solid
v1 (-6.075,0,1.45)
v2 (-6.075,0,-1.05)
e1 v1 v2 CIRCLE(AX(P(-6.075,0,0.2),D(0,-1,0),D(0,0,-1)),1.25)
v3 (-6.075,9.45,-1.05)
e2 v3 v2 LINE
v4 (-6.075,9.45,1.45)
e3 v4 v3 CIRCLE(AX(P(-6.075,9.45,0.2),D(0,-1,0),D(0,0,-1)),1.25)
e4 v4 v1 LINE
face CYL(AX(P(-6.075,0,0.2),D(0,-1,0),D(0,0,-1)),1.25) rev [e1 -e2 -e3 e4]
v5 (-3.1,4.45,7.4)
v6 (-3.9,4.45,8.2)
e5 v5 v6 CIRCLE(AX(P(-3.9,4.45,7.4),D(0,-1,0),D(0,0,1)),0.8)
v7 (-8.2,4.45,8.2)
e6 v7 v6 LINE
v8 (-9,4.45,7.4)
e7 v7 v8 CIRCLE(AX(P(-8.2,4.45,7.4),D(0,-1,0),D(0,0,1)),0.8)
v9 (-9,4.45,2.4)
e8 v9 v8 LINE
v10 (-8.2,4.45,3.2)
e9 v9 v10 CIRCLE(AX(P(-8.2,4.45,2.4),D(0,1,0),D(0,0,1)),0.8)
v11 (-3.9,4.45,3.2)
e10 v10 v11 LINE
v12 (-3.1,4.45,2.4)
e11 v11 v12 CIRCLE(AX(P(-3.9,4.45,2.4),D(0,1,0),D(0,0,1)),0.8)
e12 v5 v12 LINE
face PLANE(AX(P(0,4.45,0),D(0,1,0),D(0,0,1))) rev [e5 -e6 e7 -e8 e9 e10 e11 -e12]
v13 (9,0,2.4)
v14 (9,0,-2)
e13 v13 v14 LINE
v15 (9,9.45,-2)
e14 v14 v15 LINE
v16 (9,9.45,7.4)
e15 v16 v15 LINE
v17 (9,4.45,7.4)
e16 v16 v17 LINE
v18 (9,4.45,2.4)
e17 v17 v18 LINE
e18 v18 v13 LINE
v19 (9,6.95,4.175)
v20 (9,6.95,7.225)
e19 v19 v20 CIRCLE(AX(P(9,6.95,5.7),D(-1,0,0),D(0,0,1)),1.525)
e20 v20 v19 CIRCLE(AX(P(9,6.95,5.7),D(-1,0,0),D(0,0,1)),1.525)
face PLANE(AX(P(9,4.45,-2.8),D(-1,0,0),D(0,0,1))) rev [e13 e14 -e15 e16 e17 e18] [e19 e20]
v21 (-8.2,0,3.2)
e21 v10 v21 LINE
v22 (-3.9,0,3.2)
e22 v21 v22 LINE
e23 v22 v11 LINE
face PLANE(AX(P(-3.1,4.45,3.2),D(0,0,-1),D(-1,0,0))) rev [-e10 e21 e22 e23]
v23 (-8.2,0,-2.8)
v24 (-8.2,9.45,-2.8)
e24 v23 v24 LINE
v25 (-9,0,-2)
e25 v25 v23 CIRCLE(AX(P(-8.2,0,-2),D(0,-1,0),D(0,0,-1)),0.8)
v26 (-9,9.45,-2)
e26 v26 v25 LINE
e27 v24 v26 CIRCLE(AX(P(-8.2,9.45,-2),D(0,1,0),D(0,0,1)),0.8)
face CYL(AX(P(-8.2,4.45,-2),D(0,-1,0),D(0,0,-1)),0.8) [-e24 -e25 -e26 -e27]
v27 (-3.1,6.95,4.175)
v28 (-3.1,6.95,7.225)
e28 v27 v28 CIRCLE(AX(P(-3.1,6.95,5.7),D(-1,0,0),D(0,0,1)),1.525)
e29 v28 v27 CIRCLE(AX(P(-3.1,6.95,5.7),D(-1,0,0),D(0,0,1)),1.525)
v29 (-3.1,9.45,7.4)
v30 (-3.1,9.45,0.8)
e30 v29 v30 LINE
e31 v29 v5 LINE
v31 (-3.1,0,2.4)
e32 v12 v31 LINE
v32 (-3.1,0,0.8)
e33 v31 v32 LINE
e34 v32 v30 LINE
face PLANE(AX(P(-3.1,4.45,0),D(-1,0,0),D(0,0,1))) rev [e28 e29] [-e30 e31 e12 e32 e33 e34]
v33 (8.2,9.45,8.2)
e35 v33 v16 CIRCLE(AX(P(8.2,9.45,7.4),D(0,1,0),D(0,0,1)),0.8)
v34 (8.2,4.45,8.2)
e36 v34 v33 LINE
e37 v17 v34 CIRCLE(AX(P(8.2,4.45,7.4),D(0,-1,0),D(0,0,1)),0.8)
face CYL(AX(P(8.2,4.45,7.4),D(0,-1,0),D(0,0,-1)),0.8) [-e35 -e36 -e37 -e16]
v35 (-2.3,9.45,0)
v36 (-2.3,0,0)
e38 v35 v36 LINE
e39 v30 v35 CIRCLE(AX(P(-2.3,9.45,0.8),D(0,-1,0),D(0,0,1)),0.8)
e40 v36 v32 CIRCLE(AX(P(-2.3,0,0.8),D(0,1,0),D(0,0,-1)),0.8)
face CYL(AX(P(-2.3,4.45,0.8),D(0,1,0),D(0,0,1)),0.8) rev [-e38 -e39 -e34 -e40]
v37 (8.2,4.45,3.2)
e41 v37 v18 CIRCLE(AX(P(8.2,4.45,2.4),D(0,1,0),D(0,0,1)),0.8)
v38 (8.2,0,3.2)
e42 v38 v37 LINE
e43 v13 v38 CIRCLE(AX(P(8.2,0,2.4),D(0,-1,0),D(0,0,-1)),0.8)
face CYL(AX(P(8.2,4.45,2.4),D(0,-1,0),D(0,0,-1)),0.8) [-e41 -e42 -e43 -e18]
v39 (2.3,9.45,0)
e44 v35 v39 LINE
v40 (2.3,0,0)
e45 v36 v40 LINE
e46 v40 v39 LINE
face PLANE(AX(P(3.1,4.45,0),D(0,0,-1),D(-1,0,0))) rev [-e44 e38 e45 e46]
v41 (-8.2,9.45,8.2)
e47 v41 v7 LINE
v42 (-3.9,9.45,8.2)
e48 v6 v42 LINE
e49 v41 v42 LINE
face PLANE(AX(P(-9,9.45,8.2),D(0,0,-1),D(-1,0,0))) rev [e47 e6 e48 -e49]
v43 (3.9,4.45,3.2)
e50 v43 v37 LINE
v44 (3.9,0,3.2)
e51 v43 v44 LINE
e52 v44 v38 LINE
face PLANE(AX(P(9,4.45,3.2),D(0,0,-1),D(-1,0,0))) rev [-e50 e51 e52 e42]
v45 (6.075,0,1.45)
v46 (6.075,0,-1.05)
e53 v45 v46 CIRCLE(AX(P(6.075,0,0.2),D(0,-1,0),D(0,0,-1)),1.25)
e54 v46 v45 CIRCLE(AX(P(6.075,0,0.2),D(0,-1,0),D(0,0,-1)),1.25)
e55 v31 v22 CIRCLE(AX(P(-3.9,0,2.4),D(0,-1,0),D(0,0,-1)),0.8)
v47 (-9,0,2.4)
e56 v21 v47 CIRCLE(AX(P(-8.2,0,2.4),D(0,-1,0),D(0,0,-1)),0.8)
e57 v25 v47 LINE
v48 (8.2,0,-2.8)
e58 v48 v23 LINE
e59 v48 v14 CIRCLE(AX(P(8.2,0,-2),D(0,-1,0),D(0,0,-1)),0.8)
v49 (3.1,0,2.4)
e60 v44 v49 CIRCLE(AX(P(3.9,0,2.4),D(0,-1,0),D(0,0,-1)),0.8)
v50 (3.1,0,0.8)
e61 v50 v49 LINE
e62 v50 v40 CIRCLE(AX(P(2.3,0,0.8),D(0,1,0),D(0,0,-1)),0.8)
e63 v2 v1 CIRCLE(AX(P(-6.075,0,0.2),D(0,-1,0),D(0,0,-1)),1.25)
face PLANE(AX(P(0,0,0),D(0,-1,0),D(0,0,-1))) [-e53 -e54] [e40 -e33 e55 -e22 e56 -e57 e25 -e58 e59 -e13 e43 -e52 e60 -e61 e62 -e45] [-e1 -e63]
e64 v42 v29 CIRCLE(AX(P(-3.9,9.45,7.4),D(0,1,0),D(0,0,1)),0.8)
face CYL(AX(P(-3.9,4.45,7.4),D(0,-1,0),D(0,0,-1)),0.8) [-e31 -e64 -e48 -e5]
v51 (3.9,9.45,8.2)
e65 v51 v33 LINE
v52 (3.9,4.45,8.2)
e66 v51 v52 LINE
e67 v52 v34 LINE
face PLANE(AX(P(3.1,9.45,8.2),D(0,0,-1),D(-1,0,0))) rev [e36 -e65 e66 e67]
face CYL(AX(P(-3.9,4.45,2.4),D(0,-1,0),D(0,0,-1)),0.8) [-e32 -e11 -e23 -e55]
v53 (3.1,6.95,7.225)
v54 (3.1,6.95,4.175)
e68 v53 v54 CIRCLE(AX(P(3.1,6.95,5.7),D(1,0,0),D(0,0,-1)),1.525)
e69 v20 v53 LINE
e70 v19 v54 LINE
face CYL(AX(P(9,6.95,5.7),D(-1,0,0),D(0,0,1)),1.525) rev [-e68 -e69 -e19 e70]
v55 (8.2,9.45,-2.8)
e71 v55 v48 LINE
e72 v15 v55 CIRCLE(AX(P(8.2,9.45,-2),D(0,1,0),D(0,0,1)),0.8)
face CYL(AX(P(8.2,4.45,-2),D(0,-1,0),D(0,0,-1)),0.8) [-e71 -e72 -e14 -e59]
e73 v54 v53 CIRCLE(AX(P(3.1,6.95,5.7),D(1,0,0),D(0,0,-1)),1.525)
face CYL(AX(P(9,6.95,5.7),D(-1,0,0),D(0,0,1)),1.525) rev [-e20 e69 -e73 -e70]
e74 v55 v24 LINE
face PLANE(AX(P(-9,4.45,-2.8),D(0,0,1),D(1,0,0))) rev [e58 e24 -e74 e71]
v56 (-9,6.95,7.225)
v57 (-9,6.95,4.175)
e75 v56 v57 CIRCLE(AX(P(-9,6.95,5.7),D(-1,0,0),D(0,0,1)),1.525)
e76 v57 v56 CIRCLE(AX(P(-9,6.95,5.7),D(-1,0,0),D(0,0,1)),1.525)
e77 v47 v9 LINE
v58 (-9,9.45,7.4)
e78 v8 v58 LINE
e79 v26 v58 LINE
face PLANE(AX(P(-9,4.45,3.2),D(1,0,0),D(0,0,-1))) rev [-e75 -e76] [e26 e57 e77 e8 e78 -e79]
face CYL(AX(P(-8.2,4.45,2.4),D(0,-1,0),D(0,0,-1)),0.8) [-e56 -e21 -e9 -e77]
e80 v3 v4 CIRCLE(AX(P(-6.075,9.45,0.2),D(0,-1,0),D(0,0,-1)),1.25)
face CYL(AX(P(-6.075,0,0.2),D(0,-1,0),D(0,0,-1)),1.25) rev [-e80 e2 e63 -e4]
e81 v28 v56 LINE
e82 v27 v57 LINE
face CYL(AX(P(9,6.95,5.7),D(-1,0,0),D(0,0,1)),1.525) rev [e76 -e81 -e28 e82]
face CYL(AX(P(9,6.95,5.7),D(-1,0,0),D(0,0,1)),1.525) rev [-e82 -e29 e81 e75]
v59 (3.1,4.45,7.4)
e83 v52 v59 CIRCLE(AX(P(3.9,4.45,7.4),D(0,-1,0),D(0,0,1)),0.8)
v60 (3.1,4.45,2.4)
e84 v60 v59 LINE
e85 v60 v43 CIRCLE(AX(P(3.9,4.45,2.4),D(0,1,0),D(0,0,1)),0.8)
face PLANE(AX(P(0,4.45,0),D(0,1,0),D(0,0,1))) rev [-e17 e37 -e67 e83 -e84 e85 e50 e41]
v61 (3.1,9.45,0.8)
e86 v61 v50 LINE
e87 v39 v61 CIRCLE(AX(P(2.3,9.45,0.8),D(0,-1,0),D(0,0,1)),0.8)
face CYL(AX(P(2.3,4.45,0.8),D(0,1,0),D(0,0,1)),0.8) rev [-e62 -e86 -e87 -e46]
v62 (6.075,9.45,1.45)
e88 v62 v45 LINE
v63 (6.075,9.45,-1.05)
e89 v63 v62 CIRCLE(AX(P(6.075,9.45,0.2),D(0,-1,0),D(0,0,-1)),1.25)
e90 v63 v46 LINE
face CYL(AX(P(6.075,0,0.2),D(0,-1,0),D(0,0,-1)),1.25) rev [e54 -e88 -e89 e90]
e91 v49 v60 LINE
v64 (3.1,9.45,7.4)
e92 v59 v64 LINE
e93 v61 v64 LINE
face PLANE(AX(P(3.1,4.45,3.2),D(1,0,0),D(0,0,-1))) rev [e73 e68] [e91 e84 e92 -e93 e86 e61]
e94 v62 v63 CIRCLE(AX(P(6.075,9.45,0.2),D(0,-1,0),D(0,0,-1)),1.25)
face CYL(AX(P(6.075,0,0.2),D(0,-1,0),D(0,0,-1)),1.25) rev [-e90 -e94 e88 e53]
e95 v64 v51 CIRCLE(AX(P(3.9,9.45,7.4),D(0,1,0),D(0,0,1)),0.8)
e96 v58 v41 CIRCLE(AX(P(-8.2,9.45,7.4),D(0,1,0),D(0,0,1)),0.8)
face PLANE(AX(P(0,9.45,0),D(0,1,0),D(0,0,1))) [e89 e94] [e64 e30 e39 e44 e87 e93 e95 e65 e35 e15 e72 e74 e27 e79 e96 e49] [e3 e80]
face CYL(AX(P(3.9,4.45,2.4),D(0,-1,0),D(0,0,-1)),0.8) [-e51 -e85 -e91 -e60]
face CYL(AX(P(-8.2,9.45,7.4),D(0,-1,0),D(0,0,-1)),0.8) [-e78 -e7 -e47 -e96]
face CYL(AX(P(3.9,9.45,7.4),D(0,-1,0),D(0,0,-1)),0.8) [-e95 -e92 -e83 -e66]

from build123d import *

# Parameters (mm, degrees)
EXTRUDE_1_DEPTH     = 4.45
EXTRUDE_2_DEPTH     = 5
HOLE_WIZARD_M3_1_D  = 2.5
SKETCH_5_R          = 1.525
CUT_EXTRUDE_1_DEPTH = 22.921279616
FILLET_R0_8_1_R     = 0.8


with BuildPart() as part:
    # 草图1 → 凸台-拉伸1 (new body)
    with BuildSketch(Plane(origin=(0, 0, 0), x_dir=(1, 0, 0), z_dir=(0, 1, 0))):
        Polygon((-9, 2.8), (9, 2.8), (9, -3.2), (3.1, -3.2), (3.1, 0), (-3.1, 0), (-3.1, -3.2), (-9, -3.2), align=None)
    extrude(amount=EXTRUDE_1_DEPTH)

    # 草图2 → 凸台-拉伸2 (add)
    with BuildSketch(Plane(origin=(0, 4.45, 0), x_dir=(1, 0, 0), z_dir=(0, 1, 0))):
        Polygon((-3.1, -8.2), (-3.1, 0), (3.1, 0), (3.1, -8.2), (9, -8.2), (9, 2.8), (-9, 2.8), (-9, -8.2), align=None)
    extrude(amount=EXTRUDE_2_DEPTH)

    # M3 螺纹孔1 (through all)
    with Locations(Plane.XZ):
        with Locations((-6.075, 0.2), (6.075, 0.2)):
            Hole(HOLE_WIZARD_M3_1_D / 2)

    # 草图5 → 切除-拉伸1 (cut, through all)
    with BuildSketch(Plane.ZY.offset(9)):
        with Locations((5.7, 6.95)):
            Circle(SKETCH_5_R)
    extrude(amount=-CUT_EXTRUDE_1_DEPTH, mode=Mode.SUBTRACT)

    # R0.8 圆角1
    fillet_r0_8_1_edges = [part.edges().sort_by_distance(p)[0] for p in [
        (-9, 4.725, -2.8),
        (9, 4.725, -2.8),
        (9, 2.225, 3.2),
        (3.1, 2.225, 3.2),
        (3.1, 4.725, 0),
        (-3.1, 4.725, 0),
        (-3.1, 2.225, 3.2),
        (-9, 2.225, 3.2),
        (-9, 6.95, 8.2),
        (-3.1, 6.95, 8.2),
        (3.1, 6.95, 8.2),
        (9, 6.95, 8.2),
    ]]
    fillet(fillet_r0_8_1_edges, radius=FILLET_R0_8_1_R)


solid = part.part
